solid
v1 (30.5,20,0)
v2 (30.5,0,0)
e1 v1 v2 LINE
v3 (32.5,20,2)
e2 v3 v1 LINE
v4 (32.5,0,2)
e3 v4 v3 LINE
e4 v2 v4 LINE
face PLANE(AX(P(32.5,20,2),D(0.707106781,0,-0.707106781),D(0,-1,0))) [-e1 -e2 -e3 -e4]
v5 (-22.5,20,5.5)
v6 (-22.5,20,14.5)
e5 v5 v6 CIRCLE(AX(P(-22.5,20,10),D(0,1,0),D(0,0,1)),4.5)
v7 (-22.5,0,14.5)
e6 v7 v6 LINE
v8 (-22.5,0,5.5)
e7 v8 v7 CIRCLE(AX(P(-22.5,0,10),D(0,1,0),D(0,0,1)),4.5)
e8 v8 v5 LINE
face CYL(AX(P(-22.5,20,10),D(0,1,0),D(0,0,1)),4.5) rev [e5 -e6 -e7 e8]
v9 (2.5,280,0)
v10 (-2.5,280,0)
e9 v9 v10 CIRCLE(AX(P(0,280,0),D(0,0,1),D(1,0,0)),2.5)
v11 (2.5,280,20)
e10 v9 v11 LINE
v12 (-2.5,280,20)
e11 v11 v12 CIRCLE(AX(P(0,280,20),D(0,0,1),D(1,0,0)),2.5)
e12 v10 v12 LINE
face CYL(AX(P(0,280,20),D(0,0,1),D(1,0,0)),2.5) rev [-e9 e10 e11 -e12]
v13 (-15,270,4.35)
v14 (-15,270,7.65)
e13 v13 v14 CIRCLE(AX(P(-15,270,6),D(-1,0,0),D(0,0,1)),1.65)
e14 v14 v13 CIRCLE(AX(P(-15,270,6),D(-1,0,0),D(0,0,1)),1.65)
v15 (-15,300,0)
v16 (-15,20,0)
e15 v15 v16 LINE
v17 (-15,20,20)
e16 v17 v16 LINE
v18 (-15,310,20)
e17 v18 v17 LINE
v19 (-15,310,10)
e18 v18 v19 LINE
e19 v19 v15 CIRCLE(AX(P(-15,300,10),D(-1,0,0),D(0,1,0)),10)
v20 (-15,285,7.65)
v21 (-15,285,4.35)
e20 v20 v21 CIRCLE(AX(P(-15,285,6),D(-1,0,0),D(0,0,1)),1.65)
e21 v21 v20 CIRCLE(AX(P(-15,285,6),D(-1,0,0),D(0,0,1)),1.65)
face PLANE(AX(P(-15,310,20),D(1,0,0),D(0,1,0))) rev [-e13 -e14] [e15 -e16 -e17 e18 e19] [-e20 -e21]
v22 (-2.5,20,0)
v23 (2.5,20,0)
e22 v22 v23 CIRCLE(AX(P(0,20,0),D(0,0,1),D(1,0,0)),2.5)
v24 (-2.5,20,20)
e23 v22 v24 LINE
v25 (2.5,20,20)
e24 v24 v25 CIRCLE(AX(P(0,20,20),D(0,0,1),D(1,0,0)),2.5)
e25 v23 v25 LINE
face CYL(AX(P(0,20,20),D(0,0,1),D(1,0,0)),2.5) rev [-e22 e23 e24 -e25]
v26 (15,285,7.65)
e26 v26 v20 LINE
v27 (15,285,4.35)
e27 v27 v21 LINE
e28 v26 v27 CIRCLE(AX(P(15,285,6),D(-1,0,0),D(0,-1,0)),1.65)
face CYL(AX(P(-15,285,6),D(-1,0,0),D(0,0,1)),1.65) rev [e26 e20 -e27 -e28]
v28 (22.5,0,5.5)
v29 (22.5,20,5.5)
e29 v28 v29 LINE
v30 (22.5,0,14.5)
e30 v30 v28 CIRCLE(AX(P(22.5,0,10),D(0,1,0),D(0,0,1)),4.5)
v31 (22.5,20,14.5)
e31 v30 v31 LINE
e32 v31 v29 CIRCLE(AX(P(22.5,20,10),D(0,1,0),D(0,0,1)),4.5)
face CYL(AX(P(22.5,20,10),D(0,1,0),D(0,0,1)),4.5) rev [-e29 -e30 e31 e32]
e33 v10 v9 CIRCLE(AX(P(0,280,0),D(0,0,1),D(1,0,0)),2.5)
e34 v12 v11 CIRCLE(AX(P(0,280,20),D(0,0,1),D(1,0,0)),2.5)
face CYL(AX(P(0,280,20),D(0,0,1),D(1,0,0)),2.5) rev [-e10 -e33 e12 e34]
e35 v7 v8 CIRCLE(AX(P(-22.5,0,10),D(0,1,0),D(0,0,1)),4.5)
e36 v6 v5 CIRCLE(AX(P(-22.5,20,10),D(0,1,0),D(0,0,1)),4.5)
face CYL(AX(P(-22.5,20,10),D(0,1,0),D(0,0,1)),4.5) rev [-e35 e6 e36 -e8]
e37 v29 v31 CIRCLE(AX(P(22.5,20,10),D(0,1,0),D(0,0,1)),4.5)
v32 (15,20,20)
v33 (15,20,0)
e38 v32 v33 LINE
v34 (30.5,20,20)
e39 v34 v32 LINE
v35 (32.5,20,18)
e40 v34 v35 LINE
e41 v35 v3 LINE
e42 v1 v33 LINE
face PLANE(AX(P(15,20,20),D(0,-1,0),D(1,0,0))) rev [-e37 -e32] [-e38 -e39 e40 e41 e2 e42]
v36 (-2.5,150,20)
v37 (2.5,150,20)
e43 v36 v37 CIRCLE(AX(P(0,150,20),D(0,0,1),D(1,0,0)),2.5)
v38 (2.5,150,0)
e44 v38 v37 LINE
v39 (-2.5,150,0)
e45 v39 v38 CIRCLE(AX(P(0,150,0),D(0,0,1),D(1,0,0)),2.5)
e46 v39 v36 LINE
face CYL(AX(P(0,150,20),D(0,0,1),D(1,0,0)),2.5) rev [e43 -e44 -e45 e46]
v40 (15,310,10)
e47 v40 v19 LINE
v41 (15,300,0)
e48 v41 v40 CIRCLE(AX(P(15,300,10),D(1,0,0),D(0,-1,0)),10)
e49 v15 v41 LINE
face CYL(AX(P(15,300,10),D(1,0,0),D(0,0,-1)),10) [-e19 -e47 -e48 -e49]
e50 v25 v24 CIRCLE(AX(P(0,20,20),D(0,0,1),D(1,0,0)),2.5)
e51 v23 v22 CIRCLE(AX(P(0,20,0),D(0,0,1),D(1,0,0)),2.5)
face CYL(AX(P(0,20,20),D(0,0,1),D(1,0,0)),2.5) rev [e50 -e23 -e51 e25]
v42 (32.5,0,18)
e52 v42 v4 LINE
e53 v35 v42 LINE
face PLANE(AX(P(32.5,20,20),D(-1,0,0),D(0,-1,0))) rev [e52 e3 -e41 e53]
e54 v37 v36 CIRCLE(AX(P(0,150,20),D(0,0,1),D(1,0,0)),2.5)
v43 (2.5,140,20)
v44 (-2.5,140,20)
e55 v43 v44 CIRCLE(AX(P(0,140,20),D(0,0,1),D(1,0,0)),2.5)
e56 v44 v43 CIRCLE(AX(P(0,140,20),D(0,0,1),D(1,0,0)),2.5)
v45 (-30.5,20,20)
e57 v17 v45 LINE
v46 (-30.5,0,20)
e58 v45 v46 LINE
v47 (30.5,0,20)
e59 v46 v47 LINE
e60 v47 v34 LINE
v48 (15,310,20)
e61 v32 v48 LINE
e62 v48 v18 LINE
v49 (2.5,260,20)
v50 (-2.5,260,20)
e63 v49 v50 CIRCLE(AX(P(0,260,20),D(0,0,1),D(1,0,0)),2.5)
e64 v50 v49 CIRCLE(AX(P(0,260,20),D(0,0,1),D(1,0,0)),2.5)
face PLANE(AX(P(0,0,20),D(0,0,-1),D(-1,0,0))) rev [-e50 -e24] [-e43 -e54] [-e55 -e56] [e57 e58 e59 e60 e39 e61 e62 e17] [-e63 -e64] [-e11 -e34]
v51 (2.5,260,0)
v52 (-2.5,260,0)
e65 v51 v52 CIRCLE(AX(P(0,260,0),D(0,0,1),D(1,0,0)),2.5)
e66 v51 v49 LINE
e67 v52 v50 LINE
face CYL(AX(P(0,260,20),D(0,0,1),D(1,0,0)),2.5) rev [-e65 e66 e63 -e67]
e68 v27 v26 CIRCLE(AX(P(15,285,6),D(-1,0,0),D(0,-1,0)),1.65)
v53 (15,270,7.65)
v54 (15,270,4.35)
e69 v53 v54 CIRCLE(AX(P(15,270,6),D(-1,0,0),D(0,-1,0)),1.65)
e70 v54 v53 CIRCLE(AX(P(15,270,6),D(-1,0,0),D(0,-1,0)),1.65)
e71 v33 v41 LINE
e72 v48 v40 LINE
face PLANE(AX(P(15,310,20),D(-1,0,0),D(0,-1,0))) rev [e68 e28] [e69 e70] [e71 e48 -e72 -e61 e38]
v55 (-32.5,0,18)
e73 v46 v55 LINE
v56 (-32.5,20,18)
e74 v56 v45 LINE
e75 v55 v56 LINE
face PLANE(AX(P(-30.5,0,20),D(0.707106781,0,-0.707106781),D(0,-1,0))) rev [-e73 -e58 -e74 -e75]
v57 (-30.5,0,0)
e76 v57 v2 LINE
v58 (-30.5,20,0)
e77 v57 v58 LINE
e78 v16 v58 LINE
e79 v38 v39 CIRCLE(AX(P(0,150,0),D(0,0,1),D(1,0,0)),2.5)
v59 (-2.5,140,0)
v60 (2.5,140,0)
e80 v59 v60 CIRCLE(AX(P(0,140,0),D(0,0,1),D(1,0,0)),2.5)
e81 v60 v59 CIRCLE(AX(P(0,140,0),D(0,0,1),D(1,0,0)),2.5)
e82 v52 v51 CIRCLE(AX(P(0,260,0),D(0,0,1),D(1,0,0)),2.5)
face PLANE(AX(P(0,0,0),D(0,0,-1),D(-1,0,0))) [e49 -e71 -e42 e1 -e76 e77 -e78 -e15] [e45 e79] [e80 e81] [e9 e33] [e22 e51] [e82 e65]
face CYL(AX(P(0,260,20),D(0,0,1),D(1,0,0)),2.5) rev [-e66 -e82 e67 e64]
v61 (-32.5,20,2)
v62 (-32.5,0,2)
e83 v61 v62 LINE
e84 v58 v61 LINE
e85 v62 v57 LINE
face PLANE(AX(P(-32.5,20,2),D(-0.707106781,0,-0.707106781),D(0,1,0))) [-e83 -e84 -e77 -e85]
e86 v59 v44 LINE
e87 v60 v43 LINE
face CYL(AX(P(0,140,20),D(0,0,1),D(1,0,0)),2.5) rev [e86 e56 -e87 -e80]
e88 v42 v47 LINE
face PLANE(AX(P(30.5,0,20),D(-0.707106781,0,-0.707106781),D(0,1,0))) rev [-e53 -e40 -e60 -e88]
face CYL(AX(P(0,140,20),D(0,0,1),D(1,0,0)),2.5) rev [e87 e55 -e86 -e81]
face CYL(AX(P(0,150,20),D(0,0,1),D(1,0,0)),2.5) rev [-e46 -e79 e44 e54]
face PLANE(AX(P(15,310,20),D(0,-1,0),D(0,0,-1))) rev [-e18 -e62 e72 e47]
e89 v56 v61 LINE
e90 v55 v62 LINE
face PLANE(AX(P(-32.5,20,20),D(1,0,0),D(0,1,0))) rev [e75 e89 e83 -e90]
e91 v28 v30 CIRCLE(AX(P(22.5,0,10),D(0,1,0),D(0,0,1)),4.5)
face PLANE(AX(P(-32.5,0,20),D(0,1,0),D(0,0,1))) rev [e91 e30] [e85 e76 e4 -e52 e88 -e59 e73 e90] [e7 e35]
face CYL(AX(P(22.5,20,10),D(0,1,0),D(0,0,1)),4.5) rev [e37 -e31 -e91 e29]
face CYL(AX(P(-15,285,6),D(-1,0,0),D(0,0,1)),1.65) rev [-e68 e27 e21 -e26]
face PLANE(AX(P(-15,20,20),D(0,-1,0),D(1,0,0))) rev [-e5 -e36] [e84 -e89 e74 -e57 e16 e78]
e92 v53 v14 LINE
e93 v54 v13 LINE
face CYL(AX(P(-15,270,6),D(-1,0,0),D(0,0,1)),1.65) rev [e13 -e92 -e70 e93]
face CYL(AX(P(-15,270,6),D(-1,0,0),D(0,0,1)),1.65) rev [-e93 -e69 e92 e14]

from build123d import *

# Parameters (mm, degrees)
EXTRUDE_1_DEPTH       = 20
HOLE_WIZARD_9_0_9_1_D = 9
HOLE_WIZARD_M6_1_D    = 5
FILLET_1_R            = 10
CHAMFER_1_SIZE        = 2
HOLE_WIZARD_M4_1_D    = 3.3


with BuildPart() as part:
    # 草图1 → 凸台-拉伸1 (new body)
    with BuildSketch(Plane.XY):
        Polygon((15, 310), (-15, 310), (-15, 20), (-32.5, 20), (-32.5, 0), (32.5, 0), (32.5, 20), (15, 20), align=None)
    extrude(amount=EXTRUDE_1_DEPTH)

    # Ø9.0 (9) 直径孔1 (through all)
    with Locations(Plane(origin=(0, 20, 0), x_dir=(1, 0, 0), z_dir=(0, 1, 0))):
        with Locations((22.5, -10), (-22.5, -10)):
            Hole(HOLE_WIZARD_9_0_9_1_D / 2)

    # M6 螺纹孔1 (through all)
    with Locations(Plane.XY.offset(20)):
        with Locations((0, 280), (0, 150), (0, 20), (0, 260), (0, 140)):
            Hole(HOLE_WIZARD_M6_1_D / 2)

    # 圆角1
    fillet_1_edges = [part.edges().sort_by_distance(p)[0] for p in [
        (0, 310, 0),
    ]]
    fillet(fillet_1_edges, radius=FILLET_1_R)

    # 倒角1
    chamfer_1_edges = [part.edges().sort_by_distance(p)[0] for p in [
        (-32.5, 10, 20),
        (32.5, 10, 20),
        (32.5, 10, 0),
        (-32.5, 10, 0),
    ]]
    chamfer(chamfer_1_edges, length=CHAMFER_1_SIZE)

    # M4 螺纹孔1 (through all)
    with Locations(Plane.ZY.offset(15)):
        with Locations((6, 285), (6, 270)):
            Hole(HOLE_WIZARD_M4_1_D / 2)


solid = part.part
